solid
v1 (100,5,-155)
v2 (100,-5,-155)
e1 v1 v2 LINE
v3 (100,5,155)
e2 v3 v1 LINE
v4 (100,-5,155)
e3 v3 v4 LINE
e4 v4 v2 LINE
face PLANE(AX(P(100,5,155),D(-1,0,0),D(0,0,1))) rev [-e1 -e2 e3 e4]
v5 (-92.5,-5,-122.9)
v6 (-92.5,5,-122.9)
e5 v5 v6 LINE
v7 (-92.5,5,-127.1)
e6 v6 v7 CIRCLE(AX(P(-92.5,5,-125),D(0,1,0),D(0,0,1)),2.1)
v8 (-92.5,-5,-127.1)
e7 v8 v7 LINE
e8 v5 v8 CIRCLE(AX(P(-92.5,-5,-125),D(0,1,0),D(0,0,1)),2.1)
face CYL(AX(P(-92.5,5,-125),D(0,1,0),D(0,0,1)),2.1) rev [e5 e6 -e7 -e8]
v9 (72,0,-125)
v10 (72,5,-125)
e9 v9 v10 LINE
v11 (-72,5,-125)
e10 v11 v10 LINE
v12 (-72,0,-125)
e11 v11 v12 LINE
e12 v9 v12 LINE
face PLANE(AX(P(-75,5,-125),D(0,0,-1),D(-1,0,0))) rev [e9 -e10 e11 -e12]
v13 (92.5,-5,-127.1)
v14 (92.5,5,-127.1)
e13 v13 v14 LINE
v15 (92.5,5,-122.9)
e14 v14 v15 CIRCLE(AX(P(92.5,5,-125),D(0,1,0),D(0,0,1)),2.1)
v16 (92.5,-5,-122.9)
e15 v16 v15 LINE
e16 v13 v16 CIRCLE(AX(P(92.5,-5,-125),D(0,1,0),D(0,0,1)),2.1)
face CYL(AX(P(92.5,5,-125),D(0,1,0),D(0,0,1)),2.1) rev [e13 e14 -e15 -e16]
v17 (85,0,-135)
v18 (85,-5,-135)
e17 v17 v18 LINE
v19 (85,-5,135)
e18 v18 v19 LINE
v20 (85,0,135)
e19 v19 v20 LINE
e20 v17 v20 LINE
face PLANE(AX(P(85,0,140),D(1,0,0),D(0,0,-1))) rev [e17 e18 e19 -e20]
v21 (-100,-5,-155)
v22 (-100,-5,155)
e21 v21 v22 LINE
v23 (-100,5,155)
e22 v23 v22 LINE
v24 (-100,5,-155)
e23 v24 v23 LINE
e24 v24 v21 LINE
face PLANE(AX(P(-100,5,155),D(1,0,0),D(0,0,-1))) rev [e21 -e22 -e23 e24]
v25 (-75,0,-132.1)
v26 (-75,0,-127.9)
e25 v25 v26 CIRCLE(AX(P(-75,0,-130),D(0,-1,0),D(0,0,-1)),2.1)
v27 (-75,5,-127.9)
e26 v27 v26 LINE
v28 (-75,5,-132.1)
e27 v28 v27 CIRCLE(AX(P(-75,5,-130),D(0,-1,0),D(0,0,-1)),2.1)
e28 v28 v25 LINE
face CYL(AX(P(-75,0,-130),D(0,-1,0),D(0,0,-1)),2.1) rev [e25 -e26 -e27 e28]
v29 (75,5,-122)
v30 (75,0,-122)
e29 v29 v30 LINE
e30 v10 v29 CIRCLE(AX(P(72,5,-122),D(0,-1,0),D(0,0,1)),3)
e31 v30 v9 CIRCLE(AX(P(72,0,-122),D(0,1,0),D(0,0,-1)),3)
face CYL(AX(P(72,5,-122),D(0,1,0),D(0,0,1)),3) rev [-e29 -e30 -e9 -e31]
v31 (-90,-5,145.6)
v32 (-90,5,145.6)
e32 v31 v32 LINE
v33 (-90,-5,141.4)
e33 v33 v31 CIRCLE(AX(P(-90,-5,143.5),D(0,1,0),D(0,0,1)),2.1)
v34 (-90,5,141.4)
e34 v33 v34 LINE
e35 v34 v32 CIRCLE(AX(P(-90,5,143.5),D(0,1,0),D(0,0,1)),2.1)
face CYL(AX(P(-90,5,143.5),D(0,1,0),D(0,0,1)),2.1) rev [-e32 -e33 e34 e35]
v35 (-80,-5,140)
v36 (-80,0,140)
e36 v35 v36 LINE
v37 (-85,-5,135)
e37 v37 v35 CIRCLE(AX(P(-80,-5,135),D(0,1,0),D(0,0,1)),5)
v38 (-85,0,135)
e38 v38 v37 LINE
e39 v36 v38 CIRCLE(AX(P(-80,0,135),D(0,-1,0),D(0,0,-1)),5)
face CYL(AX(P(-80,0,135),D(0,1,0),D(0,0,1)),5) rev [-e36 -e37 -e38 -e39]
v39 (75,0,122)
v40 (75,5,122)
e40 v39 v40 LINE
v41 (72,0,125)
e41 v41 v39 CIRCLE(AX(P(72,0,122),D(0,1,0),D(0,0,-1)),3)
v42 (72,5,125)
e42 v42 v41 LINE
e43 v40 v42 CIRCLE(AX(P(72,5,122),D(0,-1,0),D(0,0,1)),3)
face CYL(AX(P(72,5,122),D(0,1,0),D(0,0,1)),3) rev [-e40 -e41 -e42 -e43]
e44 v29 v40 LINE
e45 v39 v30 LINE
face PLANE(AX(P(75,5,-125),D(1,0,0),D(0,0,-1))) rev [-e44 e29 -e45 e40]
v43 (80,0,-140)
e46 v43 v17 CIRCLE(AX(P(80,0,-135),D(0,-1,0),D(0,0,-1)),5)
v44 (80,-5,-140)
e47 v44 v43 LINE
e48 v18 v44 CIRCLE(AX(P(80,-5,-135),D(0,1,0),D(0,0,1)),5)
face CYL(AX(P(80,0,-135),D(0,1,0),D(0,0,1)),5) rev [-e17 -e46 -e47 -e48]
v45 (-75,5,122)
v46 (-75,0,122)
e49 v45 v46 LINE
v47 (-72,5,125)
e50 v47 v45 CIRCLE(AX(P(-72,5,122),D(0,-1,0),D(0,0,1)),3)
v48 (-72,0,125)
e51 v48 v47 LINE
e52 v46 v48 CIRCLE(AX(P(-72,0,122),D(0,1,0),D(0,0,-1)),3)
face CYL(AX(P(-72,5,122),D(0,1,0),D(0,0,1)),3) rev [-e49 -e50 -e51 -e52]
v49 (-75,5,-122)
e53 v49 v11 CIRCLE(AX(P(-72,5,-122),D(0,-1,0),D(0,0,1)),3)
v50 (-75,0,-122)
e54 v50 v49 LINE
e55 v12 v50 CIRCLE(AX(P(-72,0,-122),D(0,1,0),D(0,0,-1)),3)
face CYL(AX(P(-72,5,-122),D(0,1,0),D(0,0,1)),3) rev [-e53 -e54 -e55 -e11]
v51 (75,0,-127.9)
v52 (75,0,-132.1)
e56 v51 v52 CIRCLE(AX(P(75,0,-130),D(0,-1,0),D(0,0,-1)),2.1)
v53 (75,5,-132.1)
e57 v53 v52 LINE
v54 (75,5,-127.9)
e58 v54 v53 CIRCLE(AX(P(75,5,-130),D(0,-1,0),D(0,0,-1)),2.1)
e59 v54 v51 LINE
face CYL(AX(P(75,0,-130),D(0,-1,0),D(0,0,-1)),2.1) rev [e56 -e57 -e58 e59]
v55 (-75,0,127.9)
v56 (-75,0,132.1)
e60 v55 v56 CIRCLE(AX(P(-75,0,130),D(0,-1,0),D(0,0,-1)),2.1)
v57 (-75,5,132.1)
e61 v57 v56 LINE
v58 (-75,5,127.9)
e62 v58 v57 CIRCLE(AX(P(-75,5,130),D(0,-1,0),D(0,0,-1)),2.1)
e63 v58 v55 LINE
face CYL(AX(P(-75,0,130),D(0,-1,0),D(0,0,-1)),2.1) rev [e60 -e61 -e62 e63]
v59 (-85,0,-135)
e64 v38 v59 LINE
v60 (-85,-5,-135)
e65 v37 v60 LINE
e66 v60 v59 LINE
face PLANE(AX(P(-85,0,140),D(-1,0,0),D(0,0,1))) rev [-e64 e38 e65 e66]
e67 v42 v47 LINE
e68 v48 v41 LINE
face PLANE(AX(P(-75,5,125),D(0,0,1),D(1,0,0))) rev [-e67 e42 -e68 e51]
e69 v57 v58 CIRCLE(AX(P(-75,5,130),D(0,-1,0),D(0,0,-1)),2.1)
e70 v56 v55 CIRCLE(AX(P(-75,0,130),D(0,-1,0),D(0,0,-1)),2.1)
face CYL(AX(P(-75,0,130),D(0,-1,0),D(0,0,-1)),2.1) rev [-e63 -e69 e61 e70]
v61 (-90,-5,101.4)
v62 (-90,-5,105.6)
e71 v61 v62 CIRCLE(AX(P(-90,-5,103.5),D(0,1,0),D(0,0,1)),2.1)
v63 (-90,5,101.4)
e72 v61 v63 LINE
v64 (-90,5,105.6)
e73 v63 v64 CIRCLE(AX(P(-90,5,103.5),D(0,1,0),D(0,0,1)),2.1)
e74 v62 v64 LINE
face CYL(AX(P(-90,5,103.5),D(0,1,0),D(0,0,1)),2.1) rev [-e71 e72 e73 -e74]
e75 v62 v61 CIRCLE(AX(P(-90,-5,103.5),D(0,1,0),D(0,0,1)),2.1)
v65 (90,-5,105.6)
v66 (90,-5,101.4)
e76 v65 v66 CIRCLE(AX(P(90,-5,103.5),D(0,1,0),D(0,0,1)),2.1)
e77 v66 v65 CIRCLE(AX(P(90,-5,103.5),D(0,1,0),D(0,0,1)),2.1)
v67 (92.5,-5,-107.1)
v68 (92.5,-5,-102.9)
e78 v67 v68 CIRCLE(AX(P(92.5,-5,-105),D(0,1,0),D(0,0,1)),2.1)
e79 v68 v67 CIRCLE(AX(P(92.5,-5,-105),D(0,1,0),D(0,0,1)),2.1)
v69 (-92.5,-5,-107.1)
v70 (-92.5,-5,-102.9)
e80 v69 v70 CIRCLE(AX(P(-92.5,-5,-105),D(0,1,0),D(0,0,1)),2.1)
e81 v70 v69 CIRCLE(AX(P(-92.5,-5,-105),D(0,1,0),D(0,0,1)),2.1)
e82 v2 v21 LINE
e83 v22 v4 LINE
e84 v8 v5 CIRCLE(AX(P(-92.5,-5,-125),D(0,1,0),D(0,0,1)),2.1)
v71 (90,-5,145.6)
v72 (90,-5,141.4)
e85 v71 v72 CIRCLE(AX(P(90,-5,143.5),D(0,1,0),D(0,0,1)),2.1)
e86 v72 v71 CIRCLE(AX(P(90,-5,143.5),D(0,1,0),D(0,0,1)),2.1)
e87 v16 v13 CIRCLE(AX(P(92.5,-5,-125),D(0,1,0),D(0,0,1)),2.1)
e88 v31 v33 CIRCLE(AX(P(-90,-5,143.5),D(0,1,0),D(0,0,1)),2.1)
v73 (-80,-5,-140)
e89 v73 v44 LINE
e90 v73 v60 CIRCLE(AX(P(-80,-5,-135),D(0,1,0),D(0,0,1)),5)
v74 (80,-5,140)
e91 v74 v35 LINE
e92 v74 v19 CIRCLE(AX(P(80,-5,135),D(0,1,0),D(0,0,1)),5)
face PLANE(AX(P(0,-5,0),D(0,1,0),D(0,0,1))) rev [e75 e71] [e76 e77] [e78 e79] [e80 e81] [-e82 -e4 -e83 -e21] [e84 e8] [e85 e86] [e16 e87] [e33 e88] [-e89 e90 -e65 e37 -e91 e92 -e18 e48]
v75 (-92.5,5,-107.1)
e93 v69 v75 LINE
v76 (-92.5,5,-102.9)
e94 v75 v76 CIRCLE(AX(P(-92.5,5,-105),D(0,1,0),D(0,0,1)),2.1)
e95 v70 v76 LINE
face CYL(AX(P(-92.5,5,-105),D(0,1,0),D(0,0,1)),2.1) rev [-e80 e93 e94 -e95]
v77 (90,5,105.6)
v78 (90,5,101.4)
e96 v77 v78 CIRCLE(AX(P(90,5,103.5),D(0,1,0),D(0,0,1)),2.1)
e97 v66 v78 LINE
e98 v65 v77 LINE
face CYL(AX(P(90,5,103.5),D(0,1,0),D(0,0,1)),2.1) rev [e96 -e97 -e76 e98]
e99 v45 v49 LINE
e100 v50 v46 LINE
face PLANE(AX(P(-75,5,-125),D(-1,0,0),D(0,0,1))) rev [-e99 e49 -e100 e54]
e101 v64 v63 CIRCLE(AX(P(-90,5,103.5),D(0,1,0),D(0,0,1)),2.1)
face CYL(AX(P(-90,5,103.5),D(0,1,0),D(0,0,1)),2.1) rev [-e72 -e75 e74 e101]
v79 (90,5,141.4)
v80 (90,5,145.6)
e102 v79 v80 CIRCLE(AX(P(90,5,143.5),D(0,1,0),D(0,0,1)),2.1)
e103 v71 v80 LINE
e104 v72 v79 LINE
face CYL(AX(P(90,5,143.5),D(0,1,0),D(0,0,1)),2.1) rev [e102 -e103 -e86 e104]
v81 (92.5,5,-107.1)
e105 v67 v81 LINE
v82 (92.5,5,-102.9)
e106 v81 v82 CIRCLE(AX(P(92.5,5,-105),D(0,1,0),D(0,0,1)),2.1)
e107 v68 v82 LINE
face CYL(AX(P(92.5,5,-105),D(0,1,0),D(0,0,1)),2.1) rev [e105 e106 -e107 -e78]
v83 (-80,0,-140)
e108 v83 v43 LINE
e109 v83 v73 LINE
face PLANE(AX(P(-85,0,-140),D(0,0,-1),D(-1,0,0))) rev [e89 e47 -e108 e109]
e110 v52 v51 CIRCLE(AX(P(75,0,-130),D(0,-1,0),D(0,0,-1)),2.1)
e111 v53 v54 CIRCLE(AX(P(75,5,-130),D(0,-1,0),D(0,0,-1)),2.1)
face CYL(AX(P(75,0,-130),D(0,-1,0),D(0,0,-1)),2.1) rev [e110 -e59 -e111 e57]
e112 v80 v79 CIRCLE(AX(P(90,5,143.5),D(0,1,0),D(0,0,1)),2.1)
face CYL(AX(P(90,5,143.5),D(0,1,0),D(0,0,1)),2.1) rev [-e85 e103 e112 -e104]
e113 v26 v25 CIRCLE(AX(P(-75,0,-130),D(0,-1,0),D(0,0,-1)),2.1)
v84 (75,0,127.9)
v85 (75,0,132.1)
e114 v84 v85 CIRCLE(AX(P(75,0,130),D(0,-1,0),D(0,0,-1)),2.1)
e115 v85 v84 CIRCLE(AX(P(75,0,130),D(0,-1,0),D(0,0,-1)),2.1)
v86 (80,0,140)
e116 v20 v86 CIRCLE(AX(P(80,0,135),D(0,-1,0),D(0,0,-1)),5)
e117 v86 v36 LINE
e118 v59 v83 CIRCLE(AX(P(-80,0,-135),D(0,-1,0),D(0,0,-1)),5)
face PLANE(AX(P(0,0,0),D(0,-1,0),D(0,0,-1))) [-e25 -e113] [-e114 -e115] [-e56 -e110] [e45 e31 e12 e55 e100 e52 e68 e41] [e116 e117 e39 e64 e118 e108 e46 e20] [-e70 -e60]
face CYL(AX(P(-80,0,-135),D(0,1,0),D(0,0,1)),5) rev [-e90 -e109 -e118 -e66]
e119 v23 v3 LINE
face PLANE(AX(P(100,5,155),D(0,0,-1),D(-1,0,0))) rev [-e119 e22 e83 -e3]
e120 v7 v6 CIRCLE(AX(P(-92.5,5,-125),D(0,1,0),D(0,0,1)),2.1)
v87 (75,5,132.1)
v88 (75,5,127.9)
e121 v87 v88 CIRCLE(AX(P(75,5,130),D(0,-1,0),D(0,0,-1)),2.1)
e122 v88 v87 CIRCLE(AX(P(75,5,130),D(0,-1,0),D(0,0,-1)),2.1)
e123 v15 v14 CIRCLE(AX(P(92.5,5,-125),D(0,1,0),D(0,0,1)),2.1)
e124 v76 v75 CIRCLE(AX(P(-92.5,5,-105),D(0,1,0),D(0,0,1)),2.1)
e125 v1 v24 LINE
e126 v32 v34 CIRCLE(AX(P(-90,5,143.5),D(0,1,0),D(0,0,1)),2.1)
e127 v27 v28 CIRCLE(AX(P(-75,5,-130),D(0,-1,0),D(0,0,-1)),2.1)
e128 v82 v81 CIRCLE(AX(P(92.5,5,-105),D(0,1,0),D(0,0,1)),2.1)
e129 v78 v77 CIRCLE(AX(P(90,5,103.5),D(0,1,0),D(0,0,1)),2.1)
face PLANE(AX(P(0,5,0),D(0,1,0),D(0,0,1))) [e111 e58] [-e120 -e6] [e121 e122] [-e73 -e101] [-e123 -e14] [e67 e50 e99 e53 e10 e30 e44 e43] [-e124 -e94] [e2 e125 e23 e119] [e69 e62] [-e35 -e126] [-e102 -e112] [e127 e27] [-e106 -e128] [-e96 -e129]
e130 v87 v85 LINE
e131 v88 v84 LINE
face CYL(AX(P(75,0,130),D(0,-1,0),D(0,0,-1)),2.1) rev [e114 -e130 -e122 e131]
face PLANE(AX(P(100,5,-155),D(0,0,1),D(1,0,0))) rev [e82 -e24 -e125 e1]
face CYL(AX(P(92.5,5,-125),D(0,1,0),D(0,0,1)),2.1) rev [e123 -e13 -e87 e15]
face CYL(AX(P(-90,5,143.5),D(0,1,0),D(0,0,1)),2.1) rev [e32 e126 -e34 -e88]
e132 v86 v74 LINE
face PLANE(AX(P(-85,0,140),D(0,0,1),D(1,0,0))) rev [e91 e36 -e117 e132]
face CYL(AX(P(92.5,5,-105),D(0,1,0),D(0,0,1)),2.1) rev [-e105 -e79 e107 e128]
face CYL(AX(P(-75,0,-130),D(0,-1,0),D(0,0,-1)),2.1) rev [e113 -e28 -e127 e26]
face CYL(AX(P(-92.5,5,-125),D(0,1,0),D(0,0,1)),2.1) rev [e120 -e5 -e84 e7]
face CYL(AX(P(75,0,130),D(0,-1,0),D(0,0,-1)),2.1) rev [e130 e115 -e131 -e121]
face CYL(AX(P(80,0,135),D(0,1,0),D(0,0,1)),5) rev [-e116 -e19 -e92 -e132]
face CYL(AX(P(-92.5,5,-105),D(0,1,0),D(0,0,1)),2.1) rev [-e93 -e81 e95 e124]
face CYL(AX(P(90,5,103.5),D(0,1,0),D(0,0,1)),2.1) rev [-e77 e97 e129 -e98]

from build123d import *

# Parameters (mm, degrees)
SKETCH_1_W          = 200
SKETCH_1_H          = 310
EXTRUDE_1_DEPTH     = 5
SKETCH_2_W          = 150
SKETCH_2_H          = 250
CUT_EXTRUDE_1_DEPTH = 185.729532019
FILLET_1_R          = 3
SKETCH_13_W         = 170
SKETCH_13_H         = 280
CUT_EXTRUDE_2_DEPTH = 5
HOLE_WIZARD_M5_4_D  = 4.2
FILLET_2_R          = 5
HOLE_WIZARD_M5_5_D  = 4.2
HOLE_WIZARD_M5_6_D  = 4.2


with BuildPart() as part:
    # 草图1 → 凸台-拉伸1 (new, symmetric)
    with BuildSketch(Plane(origin=(0, 0, 0), x_dir=(1, 0, 0), z_dir=(0, 1, 0))):
        Rectangle(SKETCH_1_W, SKETCH_1_H)
    extrude(amount=EXTRUDE_1_DEPTH, both=True)

    # 草图2 → 切除-拉伸1 (cut, through all)
    with BuildSketch(Plane.XZ.offset(5)):
        Rectangle(SKETCH_2_W, SKETCH_2_H)
    extrude(amount=-CUT_EXTRUDE_1_DEPTH, mode=Mode.SUBTRACT)

    # 圆角1
    fillet_1_edges = [part.edges().sort_by_distance(p)[0] for p in [
        (75, 0, 125),
        (75, 0, -125),
        (-75, 0, -125),
        (-75, 0, 125),
    ]]
    fillet(fillet_1_edges, radius=FILLET_1_R)

    # 草图13 → 切除-拉伸2 (cut)
    with BuildSketch(Plane.XZ.offset(5)):
        Rectangle(SKETCH_13_W, SKETCH_13_H)
    extrude(amount=-CUT_EXTRUDE_2_DEPTH, mode=Mode.SUBTRACT)

    # M5 螺纹孔4 (through all)
    with Locations(Plane(origin=(0, 5, 0), x_dir=(1, 0, 0), z_dir=(0, 1, 0))):
        with Locations((92.5, 105), (92.5, 125), (-92.5, 105), (-92.5, 125)):
            Hole(HOLE_WIZARD_M5_4_D / 2)

    # 圆角2
    fillet_2_edges = [part.edges().sort_by_distance(p)[0] for p in [
        (85, -2.5, 140),
        (85, -2.5, -140),
        (-85, -2.5, -140),
        (-85, -2.5, 140),
    ]]
    fillet(fillet_2_edges, radius=FILLET_2_R)

    # M5 螺纹孔5 (through all)
    with Locations(Plane(origin=(0, 5, 0), x_dir=(1, 0, 0), z_dir=(0, 1, 0))):
        with Locations((-90, -103.5), (-90, -143.5), (90, -103.5), (90, -143.5)):
            Hole(HOLE_WIZARD_M5_5_D / 2)

    # M5 螺纹孔6 (through all)
    with Locations(Plane(origin=(0, 0, 0), x_dir=(-1, 0, 0), z_dir=(0, -1, 0))):
        with Locations((75, -130), (-75, -130), (75, 130), (-75, 130)):
            Hole(HOLE_WIZARD_M5_6_D / 2)


solid = part.part
